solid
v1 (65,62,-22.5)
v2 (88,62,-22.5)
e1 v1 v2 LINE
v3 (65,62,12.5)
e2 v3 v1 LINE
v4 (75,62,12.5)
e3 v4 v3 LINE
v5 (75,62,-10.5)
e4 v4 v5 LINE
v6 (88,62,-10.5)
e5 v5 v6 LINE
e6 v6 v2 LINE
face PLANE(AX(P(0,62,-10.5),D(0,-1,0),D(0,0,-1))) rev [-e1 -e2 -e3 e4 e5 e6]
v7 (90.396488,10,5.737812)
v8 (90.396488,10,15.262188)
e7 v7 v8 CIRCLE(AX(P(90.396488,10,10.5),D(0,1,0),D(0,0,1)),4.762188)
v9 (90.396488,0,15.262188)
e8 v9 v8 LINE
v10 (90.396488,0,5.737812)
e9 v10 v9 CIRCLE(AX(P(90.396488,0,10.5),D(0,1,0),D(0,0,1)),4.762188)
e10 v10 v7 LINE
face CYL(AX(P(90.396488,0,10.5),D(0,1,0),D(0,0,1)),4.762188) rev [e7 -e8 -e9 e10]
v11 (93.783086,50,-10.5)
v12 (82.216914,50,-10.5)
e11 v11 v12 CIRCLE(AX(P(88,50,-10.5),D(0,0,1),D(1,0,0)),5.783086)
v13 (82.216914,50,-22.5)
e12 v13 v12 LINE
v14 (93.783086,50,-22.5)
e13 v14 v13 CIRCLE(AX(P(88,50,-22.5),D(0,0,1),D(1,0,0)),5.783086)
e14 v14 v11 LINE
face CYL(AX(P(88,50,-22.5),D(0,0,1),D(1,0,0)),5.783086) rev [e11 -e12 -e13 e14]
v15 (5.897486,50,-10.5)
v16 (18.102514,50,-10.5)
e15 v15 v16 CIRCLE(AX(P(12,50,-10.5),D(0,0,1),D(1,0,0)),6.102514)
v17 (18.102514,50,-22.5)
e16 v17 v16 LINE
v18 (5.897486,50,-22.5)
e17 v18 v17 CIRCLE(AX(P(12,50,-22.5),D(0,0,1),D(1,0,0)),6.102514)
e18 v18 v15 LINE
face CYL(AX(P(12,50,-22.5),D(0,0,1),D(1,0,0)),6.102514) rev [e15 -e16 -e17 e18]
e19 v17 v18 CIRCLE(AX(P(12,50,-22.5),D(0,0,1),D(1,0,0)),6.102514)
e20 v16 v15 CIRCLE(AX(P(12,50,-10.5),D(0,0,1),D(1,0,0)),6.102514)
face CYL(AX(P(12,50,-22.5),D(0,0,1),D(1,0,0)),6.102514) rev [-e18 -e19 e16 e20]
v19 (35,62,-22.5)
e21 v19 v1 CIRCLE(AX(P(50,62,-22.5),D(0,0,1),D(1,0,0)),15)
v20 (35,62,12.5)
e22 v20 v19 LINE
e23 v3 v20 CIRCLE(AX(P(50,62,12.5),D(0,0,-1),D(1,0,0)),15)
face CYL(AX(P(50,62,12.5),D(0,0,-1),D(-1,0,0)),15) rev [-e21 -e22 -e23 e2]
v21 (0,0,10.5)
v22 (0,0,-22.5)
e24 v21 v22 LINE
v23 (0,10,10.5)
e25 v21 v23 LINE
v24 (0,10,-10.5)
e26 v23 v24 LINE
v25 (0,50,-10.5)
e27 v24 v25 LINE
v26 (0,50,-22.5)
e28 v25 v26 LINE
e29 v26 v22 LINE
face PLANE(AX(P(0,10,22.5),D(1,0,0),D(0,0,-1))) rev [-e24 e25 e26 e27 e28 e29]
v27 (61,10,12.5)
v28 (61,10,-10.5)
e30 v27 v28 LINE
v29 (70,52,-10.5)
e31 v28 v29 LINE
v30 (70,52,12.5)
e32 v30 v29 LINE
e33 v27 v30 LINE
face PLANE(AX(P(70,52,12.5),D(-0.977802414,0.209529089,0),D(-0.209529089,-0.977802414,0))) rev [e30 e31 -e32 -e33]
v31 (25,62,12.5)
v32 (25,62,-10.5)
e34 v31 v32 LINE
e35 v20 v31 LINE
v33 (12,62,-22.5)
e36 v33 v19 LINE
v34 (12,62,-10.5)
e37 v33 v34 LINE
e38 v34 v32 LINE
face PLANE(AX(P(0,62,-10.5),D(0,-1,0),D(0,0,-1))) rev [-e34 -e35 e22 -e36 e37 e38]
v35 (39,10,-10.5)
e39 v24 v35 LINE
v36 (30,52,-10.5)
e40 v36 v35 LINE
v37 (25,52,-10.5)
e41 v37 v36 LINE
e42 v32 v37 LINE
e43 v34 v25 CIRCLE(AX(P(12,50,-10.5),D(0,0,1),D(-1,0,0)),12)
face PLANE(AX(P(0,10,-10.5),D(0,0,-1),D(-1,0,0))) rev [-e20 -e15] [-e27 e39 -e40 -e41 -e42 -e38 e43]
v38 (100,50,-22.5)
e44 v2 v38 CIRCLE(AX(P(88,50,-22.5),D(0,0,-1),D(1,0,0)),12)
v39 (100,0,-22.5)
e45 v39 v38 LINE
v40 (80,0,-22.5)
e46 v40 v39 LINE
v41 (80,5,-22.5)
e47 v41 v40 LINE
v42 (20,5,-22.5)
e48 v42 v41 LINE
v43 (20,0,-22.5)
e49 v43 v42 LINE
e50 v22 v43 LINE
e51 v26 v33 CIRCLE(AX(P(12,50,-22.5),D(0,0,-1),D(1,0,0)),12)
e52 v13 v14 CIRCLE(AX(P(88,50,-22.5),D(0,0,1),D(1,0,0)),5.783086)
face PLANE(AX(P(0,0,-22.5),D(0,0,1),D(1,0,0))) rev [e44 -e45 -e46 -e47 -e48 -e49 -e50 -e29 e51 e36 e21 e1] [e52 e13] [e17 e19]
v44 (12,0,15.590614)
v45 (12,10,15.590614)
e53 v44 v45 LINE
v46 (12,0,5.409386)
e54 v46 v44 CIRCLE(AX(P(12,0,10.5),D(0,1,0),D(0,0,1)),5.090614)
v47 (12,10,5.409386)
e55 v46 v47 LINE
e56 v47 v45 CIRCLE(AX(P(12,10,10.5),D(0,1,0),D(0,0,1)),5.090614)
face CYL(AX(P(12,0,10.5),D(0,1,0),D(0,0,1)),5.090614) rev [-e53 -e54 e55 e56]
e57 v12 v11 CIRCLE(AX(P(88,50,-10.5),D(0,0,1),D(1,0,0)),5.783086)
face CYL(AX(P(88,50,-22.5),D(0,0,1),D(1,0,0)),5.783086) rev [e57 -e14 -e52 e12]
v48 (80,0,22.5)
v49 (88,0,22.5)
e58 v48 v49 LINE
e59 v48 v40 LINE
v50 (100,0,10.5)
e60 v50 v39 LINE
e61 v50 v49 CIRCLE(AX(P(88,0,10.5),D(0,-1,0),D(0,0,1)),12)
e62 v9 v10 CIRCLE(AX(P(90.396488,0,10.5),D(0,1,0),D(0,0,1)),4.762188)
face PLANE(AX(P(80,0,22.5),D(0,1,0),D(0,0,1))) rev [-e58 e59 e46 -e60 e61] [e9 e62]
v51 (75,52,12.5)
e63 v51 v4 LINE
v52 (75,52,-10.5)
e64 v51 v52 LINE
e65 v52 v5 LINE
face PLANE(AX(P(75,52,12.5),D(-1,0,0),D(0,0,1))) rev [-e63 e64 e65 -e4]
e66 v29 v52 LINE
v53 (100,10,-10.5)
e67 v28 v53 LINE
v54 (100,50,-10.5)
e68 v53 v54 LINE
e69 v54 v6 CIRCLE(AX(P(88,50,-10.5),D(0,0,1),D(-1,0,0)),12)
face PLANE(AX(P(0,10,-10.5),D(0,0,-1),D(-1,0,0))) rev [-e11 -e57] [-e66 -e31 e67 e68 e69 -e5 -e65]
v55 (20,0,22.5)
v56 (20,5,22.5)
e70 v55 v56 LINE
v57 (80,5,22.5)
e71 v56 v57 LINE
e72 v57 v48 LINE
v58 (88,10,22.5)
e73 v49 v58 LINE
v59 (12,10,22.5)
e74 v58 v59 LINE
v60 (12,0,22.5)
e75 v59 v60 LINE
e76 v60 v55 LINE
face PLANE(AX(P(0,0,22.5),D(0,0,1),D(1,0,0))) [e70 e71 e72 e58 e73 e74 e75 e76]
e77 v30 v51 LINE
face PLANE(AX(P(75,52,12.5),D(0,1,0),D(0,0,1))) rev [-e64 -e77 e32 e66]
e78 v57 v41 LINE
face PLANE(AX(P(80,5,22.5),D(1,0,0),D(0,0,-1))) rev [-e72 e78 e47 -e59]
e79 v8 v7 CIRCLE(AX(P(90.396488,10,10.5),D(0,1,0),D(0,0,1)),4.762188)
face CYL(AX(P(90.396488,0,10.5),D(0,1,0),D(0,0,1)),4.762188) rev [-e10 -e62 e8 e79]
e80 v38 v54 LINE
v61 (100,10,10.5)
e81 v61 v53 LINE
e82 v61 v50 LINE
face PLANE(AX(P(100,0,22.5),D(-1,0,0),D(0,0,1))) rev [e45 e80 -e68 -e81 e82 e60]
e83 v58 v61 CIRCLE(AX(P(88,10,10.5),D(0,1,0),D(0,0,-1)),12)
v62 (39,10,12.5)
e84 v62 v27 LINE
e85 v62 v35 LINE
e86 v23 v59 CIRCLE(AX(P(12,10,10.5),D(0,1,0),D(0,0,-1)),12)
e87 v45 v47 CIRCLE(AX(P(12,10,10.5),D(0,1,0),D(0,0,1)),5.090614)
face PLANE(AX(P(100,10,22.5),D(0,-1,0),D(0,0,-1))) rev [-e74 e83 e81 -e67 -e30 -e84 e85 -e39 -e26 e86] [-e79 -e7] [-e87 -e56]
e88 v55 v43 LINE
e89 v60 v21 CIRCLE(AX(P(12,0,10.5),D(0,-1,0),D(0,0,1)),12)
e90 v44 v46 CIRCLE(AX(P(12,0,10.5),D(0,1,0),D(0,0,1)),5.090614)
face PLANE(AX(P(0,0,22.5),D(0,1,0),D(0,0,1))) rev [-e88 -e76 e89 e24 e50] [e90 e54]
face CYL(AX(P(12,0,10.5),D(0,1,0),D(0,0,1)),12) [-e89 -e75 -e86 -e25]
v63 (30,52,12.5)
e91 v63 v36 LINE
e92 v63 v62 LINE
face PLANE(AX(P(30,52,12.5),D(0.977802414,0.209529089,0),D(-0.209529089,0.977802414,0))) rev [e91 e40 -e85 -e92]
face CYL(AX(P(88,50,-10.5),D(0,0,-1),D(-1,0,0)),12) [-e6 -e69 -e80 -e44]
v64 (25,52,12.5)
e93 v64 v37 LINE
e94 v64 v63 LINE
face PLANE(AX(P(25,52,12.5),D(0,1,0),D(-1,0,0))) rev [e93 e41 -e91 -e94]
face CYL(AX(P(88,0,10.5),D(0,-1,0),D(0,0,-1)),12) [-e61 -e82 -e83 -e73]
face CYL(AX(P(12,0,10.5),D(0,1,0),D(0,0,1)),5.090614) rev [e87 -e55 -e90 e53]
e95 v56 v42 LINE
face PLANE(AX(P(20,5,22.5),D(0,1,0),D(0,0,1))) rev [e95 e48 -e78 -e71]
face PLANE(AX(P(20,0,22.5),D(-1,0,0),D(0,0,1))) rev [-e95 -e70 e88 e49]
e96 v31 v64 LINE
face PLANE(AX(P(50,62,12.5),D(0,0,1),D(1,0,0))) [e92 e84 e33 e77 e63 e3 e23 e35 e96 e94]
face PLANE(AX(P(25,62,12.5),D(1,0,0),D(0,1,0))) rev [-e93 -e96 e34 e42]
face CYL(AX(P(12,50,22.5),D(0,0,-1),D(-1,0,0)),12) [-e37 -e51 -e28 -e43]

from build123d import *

# Parameters (mm, degrees)
BASE_PLATE_DEPTH               = 22.5
BACK_WALL_SKETCH_W             = 12
BACK_WALL_SKETCH_H             = 52
BACK_WALL_DEPTH                = 100
SADDLE_SUPPORT_DEPTH           = 23
WALL_HOLES_SKETCH_R            = 15
WALL_HOLES_SKETCH_R_2          = 6.102513624
WALL_HOLES_SKETCH_R_3          = 5.783086219
WALL_HOLES_DEPTH               = 123.200654663
WALL_CORNER_FILLETS_R12_R      = 12
BASE_MOUNTING_HOLES_SKETCH_R   = 5.090614353
BASE_MOUNTING_HOLES_SKETCH_R_2 = 4.76218762
BASE_MOUNTING_HOLES_DEPTH      = 115.935851674


with BuildPart() as part:
    # Base Plate Profile → Base Plate (new, symmetric)
    with BuildSketch(Plane.XY):
        Polygon((0, 0), (20, 0), (20, 5), (80, 5), (80, 0), (100, 0), (100, 10), (0, 10), align=None)
    extrude(amount=BASE_PLATE_DEPTH, both=True)

    # Back Wall Sketch → Back Wall (add)
    with BuildSketch(Plane(origin=(100, 0, 0), x_dir=(0, 0, -1), z_dir=(1, 0, 0))):
        with Locations((16.5, 36)):
            Rectangle(BACK_WALL_SKETCH_W, BACK_WALL_SKETCH_H)
    extrude(amount=-BACK_WALL_DEPTH)

    # Saddle Support Profile → Saddle Support (add)
    with BuildSketch(Plane.XY.offset(-10.5)):
        with BuildLine():
            Line((39, 10), (61, 10))
            Line((61, 10), (70, 52))
            Line((70, 52), (75, 52))
            Line((75, 52), (75, 62))
            Line((75, 62), (65, 62))
            ThreePointArc((65, 62), (50, 47), (35, 62))
            Line((35, 62), (25, 62))
            Line((25, 62), (25, 52))
            Line((25, 52), (30, 52))
            Line((30, 52), (39, 10))
        make_face()
    extrude(amount=SADDLE_SUPPORT_DEPTH)

    # Wall Holes Sketch → Wall Holes (cut, through all)
    with BuildSketch(Plane.XY.offset(-10.5)):
        with Locations((50, 62)):
            Circle(WALL_HOLES_SKETCH_R)
        with Locations((12, 50)):
            Circle(WALL_HOLES_SKETCH_R_2)
        with Locations((88, 50)):
            Circle(WALL_HOLES_SKETCH_R_3)
    extrude(amount=-WALL_HOLES_DEPTH, mode=Mode.SUBTRACT)

    # Wall Corner Fillets R12
    wall_corner_fillets_r12_edges = [part.edges().sort_by_distance(p)[0] for p in [
        (0, 5, 22.5),
        (100, 62, -16.5),
        (0, 62, -16.5),
        (100, 5, 22.5),
    ]]
    fillet(wall_corner_fillets_r12_edges, radius=WALL_CORNER_FILLETS_R12_R)

    # Base Mounting Holes Sketch → Base Mounting Holes (cut, through all)
    with BuildSketch(Plane(origin=(0, 10, 0), x_dir=(1, 0, 0), z_dir=(0, 1, 0))):
        with Locations(Location((12, -10.5, 0), (0, 0, 270))):
            Circle(BASE_MOUNTING_HOLES_SKETCH_R)
        with Locations(Location((90.396488088, -10.5, 0), (0, 0, 270))):
            Circle(BASE_MOUNTING_HOLES_SKETCH_R_2)
    extrude(amount=-BASE_MOUNTING_HOLES_DEPTH, mode=Mode.SUBTRACT)


solid = part.part
